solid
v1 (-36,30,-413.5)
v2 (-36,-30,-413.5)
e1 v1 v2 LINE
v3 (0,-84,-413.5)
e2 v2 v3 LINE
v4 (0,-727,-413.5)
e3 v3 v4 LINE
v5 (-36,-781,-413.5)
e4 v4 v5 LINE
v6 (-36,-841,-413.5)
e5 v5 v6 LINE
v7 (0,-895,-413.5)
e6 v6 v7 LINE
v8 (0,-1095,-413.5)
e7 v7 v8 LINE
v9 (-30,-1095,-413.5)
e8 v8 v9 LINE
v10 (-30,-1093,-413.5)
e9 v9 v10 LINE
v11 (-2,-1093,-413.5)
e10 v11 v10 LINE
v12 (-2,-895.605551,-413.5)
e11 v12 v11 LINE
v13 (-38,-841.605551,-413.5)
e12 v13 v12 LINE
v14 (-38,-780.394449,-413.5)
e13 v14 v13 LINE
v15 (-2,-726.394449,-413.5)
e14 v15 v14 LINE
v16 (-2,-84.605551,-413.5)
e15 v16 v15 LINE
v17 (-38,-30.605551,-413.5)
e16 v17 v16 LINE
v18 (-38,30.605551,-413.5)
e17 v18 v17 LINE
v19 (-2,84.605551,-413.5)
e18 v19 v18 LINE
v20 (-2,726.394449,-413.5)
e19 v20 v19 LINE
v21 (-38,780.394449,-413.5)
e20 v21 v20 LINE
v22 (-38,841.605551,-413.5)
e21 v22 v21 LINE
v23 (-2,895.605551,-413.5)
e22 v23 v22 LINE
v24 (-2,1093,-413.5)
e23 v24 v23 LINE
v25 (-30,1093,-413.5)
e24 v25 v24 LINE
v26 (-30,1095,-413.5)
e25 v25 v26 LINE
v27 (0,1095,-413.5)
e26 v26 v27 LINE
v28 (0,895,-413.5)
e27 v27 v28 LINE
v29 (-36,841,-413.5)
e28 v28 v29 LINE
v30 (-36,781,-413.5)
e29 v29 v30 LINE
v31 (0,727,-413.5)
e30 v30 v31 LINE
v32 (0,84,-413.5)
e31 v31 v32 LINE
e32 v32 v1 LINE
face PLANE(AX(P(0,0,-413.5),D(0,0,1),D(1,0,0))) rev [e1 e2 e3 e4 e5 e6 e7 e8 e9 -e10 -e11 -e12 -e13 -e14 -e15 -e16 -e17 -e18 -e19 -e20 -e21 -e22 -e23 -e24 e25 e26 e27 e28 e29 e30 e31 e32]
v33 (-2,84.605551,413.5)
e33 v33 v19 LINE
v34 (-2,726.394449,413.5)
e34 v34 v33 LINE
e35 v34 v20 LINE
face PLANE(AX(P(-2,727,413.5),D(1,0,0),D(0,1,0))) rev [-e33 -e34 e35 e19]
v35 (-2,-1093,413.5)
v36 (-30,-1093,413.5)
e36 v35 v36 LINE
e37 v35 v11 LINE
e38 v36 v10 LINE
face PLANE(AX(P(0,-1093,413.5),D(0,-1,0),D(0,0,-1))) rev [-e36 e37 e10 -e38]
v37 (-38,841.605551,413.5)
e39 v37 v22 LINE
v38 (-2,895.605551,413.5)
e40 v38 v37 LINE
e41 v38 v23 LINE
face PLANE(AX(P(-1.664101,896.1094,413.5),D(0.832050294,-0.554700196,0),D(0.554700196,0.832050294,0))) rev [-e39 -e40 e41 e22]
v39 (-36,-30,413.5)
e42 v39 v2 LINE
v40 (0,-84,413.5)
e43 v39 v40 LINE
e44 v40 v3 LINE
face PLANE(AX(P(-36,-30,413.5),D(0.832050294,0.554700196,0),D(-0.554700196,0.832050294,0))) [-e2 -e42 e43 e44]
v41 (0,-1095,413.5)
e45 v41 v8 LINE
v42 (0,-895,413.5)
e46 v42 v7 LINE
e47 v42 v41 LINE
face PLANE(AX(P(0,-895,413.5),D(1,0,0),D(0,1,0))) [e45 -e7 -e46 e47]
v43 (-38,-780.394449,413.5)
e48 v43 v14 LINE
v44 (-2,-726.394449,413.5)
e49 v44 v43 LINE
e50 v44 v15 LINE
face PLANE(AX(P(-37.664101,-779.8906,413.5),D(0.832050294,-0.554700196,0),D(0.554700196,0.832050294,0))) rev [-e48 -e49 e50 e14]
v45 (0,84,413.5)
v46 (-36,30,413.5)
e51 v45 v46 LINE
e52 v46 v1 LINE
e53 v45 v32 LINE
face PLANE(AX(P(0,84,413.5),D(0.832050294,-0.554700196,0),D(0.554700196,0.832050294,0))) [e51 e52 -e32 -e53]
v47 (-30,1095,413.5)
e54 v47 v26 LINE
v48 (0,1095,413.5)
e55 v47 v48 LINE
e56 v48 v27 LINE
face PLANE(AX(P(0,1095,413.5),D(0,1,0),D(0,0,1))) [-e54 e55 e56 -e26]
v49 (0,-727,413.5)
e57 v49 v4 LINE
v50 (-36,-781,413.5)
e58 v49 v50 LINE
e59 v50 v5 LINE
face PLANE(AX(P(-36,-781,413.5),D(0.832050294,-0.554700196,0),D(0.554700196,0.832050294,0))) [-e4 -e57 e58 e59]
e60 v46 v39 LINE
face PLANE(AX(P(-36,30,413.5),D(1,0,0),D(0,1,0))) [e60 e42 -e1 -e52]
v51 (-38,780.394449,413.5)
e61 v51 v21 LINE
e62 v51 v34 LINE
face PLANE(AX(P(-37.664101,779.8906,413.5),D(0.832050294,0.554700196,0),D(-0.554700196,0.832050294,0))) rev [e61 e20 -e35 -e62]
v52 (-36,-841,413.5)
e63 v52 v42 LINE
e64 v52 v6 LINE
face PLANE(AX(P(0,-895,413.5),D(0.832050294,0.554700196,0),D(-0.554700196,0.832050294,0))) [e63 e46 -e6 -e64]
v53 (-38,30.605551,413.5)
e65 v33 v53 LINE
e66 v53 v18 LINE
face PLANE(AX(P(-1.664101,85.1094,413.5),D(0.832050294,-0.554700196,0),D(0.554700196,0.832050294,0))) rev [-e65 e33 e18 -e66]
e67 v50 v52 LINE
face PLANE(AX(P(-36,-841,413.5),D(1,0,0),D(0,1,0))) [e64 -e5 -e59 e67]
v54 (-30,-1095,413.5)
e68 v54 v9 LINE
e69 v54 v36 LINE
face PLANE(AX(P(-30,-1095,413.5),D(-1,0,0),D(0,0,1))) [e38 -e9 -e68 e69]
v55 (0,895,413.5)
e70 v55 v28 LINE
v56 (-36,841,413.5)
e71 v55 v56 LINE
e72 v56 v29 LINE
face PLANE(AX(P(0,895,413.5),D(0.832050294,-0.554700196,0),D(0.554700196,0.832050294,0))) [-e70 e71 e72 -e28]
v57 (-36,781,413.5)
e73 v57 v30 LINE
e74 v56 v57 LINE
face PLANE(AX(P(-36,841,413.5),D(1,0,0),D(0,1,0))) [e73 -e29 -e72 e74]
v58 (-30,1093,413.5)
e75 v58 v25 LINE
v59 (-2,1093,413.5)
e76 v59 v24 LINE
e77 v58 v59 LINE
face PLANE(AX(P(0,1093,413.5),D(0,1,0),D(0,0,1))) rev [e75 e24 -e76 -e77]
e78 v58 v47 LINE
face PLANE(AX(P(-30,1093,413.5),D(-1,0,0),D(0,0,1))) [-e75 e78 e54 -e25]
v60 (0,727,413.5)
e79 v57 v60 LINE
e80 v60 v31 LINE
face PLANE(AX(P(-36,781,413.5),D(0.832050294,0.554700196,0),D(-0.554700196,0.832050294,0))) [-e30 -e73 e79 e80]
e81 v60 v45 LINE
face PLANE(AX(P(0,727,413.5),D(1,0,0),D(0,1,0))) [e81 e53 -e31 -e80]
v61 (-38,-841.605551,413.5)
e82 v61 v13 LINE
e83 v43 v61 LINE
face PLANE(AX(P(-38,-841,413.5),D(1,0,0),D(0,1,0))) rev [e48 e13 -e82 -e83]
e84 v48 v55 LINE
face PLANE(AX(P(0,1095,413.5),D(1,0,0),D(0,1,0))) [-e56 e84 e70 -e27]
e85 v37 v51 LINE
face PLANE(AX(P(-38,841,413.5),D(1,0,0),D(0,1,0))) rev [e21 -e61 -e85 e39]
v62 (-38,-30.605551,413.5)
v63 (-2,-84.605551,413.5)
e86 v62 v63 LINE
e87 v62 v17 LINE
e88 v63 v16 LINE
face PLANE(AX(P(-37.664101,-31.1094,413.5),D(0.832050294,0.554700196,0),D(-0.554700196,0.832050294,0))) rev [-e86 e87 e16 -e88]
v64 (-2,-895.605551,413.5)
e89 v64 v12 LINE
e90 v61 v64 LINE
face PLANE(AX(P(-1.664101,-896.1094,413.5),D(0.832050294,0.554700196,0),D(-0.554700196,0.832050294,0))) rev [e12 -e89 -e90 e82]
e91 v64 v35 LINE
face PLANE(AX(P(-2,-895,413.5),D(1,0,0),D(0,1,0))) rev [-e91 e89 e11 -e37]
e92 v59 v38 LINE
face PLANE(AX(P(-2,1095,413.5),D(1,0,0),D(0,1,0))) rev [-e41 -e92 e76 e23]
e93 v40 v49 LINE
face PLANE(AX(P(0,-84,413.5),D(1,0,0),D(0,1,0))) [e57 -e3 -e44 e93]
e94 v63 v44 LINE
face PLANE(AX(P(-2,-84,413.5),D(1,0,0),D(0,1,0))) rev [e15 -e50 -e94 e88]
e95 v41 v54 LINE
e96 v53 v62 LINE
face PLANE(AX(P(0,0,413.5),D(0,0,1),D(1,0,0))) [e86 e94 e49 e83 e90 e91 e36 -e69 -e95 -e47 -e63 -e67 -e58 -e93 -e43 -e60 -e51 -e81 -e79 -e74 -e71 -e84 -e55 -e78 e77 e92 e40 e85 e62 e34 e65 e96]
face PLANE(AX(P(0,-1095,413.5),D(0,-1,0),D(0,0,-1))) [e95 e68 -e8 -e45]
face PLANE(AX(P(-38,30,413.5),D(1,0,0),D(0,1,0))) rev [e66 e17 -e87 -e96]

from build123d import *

# Parameters (mm, degrees)
EXTRUDE_THIN1_DEPTH = 413.5


with BuildPart() as part:
    # Sketch1 → Extrude-Thin1 (new, symmetric)
    with BuildSketch(Plane.XY):
        Polygon((-30, -1095), (0, -1095), (0, -895), (-36, -841), (-36, -781), (0, -727), (0, -84), (-36, -30), (-36, 30), (0, 84), (0, 727), (-36, 781), (-36, 841), (0, 895), (0, 1095), (-30, 1095), (-30, 1093), (-2, 1093), (-2, 895.605551275), (-38, 841.605551275), (-38, 780.394448725), (-2, 726.394448725), (-2, 84.605551275), (-38, 30.605551275), (-38, -30.605551275), (-2, -84.605551275), (-2, -726.394448725), (-38, -780.394448725), (-38, -841.605551275), (-2, -895.605551275), (-2, -1093), (-30, -1093), align=None)
    extrude(amount=EXTRUDE_THIN1_DEPTH, both=True)


solid = part.part
